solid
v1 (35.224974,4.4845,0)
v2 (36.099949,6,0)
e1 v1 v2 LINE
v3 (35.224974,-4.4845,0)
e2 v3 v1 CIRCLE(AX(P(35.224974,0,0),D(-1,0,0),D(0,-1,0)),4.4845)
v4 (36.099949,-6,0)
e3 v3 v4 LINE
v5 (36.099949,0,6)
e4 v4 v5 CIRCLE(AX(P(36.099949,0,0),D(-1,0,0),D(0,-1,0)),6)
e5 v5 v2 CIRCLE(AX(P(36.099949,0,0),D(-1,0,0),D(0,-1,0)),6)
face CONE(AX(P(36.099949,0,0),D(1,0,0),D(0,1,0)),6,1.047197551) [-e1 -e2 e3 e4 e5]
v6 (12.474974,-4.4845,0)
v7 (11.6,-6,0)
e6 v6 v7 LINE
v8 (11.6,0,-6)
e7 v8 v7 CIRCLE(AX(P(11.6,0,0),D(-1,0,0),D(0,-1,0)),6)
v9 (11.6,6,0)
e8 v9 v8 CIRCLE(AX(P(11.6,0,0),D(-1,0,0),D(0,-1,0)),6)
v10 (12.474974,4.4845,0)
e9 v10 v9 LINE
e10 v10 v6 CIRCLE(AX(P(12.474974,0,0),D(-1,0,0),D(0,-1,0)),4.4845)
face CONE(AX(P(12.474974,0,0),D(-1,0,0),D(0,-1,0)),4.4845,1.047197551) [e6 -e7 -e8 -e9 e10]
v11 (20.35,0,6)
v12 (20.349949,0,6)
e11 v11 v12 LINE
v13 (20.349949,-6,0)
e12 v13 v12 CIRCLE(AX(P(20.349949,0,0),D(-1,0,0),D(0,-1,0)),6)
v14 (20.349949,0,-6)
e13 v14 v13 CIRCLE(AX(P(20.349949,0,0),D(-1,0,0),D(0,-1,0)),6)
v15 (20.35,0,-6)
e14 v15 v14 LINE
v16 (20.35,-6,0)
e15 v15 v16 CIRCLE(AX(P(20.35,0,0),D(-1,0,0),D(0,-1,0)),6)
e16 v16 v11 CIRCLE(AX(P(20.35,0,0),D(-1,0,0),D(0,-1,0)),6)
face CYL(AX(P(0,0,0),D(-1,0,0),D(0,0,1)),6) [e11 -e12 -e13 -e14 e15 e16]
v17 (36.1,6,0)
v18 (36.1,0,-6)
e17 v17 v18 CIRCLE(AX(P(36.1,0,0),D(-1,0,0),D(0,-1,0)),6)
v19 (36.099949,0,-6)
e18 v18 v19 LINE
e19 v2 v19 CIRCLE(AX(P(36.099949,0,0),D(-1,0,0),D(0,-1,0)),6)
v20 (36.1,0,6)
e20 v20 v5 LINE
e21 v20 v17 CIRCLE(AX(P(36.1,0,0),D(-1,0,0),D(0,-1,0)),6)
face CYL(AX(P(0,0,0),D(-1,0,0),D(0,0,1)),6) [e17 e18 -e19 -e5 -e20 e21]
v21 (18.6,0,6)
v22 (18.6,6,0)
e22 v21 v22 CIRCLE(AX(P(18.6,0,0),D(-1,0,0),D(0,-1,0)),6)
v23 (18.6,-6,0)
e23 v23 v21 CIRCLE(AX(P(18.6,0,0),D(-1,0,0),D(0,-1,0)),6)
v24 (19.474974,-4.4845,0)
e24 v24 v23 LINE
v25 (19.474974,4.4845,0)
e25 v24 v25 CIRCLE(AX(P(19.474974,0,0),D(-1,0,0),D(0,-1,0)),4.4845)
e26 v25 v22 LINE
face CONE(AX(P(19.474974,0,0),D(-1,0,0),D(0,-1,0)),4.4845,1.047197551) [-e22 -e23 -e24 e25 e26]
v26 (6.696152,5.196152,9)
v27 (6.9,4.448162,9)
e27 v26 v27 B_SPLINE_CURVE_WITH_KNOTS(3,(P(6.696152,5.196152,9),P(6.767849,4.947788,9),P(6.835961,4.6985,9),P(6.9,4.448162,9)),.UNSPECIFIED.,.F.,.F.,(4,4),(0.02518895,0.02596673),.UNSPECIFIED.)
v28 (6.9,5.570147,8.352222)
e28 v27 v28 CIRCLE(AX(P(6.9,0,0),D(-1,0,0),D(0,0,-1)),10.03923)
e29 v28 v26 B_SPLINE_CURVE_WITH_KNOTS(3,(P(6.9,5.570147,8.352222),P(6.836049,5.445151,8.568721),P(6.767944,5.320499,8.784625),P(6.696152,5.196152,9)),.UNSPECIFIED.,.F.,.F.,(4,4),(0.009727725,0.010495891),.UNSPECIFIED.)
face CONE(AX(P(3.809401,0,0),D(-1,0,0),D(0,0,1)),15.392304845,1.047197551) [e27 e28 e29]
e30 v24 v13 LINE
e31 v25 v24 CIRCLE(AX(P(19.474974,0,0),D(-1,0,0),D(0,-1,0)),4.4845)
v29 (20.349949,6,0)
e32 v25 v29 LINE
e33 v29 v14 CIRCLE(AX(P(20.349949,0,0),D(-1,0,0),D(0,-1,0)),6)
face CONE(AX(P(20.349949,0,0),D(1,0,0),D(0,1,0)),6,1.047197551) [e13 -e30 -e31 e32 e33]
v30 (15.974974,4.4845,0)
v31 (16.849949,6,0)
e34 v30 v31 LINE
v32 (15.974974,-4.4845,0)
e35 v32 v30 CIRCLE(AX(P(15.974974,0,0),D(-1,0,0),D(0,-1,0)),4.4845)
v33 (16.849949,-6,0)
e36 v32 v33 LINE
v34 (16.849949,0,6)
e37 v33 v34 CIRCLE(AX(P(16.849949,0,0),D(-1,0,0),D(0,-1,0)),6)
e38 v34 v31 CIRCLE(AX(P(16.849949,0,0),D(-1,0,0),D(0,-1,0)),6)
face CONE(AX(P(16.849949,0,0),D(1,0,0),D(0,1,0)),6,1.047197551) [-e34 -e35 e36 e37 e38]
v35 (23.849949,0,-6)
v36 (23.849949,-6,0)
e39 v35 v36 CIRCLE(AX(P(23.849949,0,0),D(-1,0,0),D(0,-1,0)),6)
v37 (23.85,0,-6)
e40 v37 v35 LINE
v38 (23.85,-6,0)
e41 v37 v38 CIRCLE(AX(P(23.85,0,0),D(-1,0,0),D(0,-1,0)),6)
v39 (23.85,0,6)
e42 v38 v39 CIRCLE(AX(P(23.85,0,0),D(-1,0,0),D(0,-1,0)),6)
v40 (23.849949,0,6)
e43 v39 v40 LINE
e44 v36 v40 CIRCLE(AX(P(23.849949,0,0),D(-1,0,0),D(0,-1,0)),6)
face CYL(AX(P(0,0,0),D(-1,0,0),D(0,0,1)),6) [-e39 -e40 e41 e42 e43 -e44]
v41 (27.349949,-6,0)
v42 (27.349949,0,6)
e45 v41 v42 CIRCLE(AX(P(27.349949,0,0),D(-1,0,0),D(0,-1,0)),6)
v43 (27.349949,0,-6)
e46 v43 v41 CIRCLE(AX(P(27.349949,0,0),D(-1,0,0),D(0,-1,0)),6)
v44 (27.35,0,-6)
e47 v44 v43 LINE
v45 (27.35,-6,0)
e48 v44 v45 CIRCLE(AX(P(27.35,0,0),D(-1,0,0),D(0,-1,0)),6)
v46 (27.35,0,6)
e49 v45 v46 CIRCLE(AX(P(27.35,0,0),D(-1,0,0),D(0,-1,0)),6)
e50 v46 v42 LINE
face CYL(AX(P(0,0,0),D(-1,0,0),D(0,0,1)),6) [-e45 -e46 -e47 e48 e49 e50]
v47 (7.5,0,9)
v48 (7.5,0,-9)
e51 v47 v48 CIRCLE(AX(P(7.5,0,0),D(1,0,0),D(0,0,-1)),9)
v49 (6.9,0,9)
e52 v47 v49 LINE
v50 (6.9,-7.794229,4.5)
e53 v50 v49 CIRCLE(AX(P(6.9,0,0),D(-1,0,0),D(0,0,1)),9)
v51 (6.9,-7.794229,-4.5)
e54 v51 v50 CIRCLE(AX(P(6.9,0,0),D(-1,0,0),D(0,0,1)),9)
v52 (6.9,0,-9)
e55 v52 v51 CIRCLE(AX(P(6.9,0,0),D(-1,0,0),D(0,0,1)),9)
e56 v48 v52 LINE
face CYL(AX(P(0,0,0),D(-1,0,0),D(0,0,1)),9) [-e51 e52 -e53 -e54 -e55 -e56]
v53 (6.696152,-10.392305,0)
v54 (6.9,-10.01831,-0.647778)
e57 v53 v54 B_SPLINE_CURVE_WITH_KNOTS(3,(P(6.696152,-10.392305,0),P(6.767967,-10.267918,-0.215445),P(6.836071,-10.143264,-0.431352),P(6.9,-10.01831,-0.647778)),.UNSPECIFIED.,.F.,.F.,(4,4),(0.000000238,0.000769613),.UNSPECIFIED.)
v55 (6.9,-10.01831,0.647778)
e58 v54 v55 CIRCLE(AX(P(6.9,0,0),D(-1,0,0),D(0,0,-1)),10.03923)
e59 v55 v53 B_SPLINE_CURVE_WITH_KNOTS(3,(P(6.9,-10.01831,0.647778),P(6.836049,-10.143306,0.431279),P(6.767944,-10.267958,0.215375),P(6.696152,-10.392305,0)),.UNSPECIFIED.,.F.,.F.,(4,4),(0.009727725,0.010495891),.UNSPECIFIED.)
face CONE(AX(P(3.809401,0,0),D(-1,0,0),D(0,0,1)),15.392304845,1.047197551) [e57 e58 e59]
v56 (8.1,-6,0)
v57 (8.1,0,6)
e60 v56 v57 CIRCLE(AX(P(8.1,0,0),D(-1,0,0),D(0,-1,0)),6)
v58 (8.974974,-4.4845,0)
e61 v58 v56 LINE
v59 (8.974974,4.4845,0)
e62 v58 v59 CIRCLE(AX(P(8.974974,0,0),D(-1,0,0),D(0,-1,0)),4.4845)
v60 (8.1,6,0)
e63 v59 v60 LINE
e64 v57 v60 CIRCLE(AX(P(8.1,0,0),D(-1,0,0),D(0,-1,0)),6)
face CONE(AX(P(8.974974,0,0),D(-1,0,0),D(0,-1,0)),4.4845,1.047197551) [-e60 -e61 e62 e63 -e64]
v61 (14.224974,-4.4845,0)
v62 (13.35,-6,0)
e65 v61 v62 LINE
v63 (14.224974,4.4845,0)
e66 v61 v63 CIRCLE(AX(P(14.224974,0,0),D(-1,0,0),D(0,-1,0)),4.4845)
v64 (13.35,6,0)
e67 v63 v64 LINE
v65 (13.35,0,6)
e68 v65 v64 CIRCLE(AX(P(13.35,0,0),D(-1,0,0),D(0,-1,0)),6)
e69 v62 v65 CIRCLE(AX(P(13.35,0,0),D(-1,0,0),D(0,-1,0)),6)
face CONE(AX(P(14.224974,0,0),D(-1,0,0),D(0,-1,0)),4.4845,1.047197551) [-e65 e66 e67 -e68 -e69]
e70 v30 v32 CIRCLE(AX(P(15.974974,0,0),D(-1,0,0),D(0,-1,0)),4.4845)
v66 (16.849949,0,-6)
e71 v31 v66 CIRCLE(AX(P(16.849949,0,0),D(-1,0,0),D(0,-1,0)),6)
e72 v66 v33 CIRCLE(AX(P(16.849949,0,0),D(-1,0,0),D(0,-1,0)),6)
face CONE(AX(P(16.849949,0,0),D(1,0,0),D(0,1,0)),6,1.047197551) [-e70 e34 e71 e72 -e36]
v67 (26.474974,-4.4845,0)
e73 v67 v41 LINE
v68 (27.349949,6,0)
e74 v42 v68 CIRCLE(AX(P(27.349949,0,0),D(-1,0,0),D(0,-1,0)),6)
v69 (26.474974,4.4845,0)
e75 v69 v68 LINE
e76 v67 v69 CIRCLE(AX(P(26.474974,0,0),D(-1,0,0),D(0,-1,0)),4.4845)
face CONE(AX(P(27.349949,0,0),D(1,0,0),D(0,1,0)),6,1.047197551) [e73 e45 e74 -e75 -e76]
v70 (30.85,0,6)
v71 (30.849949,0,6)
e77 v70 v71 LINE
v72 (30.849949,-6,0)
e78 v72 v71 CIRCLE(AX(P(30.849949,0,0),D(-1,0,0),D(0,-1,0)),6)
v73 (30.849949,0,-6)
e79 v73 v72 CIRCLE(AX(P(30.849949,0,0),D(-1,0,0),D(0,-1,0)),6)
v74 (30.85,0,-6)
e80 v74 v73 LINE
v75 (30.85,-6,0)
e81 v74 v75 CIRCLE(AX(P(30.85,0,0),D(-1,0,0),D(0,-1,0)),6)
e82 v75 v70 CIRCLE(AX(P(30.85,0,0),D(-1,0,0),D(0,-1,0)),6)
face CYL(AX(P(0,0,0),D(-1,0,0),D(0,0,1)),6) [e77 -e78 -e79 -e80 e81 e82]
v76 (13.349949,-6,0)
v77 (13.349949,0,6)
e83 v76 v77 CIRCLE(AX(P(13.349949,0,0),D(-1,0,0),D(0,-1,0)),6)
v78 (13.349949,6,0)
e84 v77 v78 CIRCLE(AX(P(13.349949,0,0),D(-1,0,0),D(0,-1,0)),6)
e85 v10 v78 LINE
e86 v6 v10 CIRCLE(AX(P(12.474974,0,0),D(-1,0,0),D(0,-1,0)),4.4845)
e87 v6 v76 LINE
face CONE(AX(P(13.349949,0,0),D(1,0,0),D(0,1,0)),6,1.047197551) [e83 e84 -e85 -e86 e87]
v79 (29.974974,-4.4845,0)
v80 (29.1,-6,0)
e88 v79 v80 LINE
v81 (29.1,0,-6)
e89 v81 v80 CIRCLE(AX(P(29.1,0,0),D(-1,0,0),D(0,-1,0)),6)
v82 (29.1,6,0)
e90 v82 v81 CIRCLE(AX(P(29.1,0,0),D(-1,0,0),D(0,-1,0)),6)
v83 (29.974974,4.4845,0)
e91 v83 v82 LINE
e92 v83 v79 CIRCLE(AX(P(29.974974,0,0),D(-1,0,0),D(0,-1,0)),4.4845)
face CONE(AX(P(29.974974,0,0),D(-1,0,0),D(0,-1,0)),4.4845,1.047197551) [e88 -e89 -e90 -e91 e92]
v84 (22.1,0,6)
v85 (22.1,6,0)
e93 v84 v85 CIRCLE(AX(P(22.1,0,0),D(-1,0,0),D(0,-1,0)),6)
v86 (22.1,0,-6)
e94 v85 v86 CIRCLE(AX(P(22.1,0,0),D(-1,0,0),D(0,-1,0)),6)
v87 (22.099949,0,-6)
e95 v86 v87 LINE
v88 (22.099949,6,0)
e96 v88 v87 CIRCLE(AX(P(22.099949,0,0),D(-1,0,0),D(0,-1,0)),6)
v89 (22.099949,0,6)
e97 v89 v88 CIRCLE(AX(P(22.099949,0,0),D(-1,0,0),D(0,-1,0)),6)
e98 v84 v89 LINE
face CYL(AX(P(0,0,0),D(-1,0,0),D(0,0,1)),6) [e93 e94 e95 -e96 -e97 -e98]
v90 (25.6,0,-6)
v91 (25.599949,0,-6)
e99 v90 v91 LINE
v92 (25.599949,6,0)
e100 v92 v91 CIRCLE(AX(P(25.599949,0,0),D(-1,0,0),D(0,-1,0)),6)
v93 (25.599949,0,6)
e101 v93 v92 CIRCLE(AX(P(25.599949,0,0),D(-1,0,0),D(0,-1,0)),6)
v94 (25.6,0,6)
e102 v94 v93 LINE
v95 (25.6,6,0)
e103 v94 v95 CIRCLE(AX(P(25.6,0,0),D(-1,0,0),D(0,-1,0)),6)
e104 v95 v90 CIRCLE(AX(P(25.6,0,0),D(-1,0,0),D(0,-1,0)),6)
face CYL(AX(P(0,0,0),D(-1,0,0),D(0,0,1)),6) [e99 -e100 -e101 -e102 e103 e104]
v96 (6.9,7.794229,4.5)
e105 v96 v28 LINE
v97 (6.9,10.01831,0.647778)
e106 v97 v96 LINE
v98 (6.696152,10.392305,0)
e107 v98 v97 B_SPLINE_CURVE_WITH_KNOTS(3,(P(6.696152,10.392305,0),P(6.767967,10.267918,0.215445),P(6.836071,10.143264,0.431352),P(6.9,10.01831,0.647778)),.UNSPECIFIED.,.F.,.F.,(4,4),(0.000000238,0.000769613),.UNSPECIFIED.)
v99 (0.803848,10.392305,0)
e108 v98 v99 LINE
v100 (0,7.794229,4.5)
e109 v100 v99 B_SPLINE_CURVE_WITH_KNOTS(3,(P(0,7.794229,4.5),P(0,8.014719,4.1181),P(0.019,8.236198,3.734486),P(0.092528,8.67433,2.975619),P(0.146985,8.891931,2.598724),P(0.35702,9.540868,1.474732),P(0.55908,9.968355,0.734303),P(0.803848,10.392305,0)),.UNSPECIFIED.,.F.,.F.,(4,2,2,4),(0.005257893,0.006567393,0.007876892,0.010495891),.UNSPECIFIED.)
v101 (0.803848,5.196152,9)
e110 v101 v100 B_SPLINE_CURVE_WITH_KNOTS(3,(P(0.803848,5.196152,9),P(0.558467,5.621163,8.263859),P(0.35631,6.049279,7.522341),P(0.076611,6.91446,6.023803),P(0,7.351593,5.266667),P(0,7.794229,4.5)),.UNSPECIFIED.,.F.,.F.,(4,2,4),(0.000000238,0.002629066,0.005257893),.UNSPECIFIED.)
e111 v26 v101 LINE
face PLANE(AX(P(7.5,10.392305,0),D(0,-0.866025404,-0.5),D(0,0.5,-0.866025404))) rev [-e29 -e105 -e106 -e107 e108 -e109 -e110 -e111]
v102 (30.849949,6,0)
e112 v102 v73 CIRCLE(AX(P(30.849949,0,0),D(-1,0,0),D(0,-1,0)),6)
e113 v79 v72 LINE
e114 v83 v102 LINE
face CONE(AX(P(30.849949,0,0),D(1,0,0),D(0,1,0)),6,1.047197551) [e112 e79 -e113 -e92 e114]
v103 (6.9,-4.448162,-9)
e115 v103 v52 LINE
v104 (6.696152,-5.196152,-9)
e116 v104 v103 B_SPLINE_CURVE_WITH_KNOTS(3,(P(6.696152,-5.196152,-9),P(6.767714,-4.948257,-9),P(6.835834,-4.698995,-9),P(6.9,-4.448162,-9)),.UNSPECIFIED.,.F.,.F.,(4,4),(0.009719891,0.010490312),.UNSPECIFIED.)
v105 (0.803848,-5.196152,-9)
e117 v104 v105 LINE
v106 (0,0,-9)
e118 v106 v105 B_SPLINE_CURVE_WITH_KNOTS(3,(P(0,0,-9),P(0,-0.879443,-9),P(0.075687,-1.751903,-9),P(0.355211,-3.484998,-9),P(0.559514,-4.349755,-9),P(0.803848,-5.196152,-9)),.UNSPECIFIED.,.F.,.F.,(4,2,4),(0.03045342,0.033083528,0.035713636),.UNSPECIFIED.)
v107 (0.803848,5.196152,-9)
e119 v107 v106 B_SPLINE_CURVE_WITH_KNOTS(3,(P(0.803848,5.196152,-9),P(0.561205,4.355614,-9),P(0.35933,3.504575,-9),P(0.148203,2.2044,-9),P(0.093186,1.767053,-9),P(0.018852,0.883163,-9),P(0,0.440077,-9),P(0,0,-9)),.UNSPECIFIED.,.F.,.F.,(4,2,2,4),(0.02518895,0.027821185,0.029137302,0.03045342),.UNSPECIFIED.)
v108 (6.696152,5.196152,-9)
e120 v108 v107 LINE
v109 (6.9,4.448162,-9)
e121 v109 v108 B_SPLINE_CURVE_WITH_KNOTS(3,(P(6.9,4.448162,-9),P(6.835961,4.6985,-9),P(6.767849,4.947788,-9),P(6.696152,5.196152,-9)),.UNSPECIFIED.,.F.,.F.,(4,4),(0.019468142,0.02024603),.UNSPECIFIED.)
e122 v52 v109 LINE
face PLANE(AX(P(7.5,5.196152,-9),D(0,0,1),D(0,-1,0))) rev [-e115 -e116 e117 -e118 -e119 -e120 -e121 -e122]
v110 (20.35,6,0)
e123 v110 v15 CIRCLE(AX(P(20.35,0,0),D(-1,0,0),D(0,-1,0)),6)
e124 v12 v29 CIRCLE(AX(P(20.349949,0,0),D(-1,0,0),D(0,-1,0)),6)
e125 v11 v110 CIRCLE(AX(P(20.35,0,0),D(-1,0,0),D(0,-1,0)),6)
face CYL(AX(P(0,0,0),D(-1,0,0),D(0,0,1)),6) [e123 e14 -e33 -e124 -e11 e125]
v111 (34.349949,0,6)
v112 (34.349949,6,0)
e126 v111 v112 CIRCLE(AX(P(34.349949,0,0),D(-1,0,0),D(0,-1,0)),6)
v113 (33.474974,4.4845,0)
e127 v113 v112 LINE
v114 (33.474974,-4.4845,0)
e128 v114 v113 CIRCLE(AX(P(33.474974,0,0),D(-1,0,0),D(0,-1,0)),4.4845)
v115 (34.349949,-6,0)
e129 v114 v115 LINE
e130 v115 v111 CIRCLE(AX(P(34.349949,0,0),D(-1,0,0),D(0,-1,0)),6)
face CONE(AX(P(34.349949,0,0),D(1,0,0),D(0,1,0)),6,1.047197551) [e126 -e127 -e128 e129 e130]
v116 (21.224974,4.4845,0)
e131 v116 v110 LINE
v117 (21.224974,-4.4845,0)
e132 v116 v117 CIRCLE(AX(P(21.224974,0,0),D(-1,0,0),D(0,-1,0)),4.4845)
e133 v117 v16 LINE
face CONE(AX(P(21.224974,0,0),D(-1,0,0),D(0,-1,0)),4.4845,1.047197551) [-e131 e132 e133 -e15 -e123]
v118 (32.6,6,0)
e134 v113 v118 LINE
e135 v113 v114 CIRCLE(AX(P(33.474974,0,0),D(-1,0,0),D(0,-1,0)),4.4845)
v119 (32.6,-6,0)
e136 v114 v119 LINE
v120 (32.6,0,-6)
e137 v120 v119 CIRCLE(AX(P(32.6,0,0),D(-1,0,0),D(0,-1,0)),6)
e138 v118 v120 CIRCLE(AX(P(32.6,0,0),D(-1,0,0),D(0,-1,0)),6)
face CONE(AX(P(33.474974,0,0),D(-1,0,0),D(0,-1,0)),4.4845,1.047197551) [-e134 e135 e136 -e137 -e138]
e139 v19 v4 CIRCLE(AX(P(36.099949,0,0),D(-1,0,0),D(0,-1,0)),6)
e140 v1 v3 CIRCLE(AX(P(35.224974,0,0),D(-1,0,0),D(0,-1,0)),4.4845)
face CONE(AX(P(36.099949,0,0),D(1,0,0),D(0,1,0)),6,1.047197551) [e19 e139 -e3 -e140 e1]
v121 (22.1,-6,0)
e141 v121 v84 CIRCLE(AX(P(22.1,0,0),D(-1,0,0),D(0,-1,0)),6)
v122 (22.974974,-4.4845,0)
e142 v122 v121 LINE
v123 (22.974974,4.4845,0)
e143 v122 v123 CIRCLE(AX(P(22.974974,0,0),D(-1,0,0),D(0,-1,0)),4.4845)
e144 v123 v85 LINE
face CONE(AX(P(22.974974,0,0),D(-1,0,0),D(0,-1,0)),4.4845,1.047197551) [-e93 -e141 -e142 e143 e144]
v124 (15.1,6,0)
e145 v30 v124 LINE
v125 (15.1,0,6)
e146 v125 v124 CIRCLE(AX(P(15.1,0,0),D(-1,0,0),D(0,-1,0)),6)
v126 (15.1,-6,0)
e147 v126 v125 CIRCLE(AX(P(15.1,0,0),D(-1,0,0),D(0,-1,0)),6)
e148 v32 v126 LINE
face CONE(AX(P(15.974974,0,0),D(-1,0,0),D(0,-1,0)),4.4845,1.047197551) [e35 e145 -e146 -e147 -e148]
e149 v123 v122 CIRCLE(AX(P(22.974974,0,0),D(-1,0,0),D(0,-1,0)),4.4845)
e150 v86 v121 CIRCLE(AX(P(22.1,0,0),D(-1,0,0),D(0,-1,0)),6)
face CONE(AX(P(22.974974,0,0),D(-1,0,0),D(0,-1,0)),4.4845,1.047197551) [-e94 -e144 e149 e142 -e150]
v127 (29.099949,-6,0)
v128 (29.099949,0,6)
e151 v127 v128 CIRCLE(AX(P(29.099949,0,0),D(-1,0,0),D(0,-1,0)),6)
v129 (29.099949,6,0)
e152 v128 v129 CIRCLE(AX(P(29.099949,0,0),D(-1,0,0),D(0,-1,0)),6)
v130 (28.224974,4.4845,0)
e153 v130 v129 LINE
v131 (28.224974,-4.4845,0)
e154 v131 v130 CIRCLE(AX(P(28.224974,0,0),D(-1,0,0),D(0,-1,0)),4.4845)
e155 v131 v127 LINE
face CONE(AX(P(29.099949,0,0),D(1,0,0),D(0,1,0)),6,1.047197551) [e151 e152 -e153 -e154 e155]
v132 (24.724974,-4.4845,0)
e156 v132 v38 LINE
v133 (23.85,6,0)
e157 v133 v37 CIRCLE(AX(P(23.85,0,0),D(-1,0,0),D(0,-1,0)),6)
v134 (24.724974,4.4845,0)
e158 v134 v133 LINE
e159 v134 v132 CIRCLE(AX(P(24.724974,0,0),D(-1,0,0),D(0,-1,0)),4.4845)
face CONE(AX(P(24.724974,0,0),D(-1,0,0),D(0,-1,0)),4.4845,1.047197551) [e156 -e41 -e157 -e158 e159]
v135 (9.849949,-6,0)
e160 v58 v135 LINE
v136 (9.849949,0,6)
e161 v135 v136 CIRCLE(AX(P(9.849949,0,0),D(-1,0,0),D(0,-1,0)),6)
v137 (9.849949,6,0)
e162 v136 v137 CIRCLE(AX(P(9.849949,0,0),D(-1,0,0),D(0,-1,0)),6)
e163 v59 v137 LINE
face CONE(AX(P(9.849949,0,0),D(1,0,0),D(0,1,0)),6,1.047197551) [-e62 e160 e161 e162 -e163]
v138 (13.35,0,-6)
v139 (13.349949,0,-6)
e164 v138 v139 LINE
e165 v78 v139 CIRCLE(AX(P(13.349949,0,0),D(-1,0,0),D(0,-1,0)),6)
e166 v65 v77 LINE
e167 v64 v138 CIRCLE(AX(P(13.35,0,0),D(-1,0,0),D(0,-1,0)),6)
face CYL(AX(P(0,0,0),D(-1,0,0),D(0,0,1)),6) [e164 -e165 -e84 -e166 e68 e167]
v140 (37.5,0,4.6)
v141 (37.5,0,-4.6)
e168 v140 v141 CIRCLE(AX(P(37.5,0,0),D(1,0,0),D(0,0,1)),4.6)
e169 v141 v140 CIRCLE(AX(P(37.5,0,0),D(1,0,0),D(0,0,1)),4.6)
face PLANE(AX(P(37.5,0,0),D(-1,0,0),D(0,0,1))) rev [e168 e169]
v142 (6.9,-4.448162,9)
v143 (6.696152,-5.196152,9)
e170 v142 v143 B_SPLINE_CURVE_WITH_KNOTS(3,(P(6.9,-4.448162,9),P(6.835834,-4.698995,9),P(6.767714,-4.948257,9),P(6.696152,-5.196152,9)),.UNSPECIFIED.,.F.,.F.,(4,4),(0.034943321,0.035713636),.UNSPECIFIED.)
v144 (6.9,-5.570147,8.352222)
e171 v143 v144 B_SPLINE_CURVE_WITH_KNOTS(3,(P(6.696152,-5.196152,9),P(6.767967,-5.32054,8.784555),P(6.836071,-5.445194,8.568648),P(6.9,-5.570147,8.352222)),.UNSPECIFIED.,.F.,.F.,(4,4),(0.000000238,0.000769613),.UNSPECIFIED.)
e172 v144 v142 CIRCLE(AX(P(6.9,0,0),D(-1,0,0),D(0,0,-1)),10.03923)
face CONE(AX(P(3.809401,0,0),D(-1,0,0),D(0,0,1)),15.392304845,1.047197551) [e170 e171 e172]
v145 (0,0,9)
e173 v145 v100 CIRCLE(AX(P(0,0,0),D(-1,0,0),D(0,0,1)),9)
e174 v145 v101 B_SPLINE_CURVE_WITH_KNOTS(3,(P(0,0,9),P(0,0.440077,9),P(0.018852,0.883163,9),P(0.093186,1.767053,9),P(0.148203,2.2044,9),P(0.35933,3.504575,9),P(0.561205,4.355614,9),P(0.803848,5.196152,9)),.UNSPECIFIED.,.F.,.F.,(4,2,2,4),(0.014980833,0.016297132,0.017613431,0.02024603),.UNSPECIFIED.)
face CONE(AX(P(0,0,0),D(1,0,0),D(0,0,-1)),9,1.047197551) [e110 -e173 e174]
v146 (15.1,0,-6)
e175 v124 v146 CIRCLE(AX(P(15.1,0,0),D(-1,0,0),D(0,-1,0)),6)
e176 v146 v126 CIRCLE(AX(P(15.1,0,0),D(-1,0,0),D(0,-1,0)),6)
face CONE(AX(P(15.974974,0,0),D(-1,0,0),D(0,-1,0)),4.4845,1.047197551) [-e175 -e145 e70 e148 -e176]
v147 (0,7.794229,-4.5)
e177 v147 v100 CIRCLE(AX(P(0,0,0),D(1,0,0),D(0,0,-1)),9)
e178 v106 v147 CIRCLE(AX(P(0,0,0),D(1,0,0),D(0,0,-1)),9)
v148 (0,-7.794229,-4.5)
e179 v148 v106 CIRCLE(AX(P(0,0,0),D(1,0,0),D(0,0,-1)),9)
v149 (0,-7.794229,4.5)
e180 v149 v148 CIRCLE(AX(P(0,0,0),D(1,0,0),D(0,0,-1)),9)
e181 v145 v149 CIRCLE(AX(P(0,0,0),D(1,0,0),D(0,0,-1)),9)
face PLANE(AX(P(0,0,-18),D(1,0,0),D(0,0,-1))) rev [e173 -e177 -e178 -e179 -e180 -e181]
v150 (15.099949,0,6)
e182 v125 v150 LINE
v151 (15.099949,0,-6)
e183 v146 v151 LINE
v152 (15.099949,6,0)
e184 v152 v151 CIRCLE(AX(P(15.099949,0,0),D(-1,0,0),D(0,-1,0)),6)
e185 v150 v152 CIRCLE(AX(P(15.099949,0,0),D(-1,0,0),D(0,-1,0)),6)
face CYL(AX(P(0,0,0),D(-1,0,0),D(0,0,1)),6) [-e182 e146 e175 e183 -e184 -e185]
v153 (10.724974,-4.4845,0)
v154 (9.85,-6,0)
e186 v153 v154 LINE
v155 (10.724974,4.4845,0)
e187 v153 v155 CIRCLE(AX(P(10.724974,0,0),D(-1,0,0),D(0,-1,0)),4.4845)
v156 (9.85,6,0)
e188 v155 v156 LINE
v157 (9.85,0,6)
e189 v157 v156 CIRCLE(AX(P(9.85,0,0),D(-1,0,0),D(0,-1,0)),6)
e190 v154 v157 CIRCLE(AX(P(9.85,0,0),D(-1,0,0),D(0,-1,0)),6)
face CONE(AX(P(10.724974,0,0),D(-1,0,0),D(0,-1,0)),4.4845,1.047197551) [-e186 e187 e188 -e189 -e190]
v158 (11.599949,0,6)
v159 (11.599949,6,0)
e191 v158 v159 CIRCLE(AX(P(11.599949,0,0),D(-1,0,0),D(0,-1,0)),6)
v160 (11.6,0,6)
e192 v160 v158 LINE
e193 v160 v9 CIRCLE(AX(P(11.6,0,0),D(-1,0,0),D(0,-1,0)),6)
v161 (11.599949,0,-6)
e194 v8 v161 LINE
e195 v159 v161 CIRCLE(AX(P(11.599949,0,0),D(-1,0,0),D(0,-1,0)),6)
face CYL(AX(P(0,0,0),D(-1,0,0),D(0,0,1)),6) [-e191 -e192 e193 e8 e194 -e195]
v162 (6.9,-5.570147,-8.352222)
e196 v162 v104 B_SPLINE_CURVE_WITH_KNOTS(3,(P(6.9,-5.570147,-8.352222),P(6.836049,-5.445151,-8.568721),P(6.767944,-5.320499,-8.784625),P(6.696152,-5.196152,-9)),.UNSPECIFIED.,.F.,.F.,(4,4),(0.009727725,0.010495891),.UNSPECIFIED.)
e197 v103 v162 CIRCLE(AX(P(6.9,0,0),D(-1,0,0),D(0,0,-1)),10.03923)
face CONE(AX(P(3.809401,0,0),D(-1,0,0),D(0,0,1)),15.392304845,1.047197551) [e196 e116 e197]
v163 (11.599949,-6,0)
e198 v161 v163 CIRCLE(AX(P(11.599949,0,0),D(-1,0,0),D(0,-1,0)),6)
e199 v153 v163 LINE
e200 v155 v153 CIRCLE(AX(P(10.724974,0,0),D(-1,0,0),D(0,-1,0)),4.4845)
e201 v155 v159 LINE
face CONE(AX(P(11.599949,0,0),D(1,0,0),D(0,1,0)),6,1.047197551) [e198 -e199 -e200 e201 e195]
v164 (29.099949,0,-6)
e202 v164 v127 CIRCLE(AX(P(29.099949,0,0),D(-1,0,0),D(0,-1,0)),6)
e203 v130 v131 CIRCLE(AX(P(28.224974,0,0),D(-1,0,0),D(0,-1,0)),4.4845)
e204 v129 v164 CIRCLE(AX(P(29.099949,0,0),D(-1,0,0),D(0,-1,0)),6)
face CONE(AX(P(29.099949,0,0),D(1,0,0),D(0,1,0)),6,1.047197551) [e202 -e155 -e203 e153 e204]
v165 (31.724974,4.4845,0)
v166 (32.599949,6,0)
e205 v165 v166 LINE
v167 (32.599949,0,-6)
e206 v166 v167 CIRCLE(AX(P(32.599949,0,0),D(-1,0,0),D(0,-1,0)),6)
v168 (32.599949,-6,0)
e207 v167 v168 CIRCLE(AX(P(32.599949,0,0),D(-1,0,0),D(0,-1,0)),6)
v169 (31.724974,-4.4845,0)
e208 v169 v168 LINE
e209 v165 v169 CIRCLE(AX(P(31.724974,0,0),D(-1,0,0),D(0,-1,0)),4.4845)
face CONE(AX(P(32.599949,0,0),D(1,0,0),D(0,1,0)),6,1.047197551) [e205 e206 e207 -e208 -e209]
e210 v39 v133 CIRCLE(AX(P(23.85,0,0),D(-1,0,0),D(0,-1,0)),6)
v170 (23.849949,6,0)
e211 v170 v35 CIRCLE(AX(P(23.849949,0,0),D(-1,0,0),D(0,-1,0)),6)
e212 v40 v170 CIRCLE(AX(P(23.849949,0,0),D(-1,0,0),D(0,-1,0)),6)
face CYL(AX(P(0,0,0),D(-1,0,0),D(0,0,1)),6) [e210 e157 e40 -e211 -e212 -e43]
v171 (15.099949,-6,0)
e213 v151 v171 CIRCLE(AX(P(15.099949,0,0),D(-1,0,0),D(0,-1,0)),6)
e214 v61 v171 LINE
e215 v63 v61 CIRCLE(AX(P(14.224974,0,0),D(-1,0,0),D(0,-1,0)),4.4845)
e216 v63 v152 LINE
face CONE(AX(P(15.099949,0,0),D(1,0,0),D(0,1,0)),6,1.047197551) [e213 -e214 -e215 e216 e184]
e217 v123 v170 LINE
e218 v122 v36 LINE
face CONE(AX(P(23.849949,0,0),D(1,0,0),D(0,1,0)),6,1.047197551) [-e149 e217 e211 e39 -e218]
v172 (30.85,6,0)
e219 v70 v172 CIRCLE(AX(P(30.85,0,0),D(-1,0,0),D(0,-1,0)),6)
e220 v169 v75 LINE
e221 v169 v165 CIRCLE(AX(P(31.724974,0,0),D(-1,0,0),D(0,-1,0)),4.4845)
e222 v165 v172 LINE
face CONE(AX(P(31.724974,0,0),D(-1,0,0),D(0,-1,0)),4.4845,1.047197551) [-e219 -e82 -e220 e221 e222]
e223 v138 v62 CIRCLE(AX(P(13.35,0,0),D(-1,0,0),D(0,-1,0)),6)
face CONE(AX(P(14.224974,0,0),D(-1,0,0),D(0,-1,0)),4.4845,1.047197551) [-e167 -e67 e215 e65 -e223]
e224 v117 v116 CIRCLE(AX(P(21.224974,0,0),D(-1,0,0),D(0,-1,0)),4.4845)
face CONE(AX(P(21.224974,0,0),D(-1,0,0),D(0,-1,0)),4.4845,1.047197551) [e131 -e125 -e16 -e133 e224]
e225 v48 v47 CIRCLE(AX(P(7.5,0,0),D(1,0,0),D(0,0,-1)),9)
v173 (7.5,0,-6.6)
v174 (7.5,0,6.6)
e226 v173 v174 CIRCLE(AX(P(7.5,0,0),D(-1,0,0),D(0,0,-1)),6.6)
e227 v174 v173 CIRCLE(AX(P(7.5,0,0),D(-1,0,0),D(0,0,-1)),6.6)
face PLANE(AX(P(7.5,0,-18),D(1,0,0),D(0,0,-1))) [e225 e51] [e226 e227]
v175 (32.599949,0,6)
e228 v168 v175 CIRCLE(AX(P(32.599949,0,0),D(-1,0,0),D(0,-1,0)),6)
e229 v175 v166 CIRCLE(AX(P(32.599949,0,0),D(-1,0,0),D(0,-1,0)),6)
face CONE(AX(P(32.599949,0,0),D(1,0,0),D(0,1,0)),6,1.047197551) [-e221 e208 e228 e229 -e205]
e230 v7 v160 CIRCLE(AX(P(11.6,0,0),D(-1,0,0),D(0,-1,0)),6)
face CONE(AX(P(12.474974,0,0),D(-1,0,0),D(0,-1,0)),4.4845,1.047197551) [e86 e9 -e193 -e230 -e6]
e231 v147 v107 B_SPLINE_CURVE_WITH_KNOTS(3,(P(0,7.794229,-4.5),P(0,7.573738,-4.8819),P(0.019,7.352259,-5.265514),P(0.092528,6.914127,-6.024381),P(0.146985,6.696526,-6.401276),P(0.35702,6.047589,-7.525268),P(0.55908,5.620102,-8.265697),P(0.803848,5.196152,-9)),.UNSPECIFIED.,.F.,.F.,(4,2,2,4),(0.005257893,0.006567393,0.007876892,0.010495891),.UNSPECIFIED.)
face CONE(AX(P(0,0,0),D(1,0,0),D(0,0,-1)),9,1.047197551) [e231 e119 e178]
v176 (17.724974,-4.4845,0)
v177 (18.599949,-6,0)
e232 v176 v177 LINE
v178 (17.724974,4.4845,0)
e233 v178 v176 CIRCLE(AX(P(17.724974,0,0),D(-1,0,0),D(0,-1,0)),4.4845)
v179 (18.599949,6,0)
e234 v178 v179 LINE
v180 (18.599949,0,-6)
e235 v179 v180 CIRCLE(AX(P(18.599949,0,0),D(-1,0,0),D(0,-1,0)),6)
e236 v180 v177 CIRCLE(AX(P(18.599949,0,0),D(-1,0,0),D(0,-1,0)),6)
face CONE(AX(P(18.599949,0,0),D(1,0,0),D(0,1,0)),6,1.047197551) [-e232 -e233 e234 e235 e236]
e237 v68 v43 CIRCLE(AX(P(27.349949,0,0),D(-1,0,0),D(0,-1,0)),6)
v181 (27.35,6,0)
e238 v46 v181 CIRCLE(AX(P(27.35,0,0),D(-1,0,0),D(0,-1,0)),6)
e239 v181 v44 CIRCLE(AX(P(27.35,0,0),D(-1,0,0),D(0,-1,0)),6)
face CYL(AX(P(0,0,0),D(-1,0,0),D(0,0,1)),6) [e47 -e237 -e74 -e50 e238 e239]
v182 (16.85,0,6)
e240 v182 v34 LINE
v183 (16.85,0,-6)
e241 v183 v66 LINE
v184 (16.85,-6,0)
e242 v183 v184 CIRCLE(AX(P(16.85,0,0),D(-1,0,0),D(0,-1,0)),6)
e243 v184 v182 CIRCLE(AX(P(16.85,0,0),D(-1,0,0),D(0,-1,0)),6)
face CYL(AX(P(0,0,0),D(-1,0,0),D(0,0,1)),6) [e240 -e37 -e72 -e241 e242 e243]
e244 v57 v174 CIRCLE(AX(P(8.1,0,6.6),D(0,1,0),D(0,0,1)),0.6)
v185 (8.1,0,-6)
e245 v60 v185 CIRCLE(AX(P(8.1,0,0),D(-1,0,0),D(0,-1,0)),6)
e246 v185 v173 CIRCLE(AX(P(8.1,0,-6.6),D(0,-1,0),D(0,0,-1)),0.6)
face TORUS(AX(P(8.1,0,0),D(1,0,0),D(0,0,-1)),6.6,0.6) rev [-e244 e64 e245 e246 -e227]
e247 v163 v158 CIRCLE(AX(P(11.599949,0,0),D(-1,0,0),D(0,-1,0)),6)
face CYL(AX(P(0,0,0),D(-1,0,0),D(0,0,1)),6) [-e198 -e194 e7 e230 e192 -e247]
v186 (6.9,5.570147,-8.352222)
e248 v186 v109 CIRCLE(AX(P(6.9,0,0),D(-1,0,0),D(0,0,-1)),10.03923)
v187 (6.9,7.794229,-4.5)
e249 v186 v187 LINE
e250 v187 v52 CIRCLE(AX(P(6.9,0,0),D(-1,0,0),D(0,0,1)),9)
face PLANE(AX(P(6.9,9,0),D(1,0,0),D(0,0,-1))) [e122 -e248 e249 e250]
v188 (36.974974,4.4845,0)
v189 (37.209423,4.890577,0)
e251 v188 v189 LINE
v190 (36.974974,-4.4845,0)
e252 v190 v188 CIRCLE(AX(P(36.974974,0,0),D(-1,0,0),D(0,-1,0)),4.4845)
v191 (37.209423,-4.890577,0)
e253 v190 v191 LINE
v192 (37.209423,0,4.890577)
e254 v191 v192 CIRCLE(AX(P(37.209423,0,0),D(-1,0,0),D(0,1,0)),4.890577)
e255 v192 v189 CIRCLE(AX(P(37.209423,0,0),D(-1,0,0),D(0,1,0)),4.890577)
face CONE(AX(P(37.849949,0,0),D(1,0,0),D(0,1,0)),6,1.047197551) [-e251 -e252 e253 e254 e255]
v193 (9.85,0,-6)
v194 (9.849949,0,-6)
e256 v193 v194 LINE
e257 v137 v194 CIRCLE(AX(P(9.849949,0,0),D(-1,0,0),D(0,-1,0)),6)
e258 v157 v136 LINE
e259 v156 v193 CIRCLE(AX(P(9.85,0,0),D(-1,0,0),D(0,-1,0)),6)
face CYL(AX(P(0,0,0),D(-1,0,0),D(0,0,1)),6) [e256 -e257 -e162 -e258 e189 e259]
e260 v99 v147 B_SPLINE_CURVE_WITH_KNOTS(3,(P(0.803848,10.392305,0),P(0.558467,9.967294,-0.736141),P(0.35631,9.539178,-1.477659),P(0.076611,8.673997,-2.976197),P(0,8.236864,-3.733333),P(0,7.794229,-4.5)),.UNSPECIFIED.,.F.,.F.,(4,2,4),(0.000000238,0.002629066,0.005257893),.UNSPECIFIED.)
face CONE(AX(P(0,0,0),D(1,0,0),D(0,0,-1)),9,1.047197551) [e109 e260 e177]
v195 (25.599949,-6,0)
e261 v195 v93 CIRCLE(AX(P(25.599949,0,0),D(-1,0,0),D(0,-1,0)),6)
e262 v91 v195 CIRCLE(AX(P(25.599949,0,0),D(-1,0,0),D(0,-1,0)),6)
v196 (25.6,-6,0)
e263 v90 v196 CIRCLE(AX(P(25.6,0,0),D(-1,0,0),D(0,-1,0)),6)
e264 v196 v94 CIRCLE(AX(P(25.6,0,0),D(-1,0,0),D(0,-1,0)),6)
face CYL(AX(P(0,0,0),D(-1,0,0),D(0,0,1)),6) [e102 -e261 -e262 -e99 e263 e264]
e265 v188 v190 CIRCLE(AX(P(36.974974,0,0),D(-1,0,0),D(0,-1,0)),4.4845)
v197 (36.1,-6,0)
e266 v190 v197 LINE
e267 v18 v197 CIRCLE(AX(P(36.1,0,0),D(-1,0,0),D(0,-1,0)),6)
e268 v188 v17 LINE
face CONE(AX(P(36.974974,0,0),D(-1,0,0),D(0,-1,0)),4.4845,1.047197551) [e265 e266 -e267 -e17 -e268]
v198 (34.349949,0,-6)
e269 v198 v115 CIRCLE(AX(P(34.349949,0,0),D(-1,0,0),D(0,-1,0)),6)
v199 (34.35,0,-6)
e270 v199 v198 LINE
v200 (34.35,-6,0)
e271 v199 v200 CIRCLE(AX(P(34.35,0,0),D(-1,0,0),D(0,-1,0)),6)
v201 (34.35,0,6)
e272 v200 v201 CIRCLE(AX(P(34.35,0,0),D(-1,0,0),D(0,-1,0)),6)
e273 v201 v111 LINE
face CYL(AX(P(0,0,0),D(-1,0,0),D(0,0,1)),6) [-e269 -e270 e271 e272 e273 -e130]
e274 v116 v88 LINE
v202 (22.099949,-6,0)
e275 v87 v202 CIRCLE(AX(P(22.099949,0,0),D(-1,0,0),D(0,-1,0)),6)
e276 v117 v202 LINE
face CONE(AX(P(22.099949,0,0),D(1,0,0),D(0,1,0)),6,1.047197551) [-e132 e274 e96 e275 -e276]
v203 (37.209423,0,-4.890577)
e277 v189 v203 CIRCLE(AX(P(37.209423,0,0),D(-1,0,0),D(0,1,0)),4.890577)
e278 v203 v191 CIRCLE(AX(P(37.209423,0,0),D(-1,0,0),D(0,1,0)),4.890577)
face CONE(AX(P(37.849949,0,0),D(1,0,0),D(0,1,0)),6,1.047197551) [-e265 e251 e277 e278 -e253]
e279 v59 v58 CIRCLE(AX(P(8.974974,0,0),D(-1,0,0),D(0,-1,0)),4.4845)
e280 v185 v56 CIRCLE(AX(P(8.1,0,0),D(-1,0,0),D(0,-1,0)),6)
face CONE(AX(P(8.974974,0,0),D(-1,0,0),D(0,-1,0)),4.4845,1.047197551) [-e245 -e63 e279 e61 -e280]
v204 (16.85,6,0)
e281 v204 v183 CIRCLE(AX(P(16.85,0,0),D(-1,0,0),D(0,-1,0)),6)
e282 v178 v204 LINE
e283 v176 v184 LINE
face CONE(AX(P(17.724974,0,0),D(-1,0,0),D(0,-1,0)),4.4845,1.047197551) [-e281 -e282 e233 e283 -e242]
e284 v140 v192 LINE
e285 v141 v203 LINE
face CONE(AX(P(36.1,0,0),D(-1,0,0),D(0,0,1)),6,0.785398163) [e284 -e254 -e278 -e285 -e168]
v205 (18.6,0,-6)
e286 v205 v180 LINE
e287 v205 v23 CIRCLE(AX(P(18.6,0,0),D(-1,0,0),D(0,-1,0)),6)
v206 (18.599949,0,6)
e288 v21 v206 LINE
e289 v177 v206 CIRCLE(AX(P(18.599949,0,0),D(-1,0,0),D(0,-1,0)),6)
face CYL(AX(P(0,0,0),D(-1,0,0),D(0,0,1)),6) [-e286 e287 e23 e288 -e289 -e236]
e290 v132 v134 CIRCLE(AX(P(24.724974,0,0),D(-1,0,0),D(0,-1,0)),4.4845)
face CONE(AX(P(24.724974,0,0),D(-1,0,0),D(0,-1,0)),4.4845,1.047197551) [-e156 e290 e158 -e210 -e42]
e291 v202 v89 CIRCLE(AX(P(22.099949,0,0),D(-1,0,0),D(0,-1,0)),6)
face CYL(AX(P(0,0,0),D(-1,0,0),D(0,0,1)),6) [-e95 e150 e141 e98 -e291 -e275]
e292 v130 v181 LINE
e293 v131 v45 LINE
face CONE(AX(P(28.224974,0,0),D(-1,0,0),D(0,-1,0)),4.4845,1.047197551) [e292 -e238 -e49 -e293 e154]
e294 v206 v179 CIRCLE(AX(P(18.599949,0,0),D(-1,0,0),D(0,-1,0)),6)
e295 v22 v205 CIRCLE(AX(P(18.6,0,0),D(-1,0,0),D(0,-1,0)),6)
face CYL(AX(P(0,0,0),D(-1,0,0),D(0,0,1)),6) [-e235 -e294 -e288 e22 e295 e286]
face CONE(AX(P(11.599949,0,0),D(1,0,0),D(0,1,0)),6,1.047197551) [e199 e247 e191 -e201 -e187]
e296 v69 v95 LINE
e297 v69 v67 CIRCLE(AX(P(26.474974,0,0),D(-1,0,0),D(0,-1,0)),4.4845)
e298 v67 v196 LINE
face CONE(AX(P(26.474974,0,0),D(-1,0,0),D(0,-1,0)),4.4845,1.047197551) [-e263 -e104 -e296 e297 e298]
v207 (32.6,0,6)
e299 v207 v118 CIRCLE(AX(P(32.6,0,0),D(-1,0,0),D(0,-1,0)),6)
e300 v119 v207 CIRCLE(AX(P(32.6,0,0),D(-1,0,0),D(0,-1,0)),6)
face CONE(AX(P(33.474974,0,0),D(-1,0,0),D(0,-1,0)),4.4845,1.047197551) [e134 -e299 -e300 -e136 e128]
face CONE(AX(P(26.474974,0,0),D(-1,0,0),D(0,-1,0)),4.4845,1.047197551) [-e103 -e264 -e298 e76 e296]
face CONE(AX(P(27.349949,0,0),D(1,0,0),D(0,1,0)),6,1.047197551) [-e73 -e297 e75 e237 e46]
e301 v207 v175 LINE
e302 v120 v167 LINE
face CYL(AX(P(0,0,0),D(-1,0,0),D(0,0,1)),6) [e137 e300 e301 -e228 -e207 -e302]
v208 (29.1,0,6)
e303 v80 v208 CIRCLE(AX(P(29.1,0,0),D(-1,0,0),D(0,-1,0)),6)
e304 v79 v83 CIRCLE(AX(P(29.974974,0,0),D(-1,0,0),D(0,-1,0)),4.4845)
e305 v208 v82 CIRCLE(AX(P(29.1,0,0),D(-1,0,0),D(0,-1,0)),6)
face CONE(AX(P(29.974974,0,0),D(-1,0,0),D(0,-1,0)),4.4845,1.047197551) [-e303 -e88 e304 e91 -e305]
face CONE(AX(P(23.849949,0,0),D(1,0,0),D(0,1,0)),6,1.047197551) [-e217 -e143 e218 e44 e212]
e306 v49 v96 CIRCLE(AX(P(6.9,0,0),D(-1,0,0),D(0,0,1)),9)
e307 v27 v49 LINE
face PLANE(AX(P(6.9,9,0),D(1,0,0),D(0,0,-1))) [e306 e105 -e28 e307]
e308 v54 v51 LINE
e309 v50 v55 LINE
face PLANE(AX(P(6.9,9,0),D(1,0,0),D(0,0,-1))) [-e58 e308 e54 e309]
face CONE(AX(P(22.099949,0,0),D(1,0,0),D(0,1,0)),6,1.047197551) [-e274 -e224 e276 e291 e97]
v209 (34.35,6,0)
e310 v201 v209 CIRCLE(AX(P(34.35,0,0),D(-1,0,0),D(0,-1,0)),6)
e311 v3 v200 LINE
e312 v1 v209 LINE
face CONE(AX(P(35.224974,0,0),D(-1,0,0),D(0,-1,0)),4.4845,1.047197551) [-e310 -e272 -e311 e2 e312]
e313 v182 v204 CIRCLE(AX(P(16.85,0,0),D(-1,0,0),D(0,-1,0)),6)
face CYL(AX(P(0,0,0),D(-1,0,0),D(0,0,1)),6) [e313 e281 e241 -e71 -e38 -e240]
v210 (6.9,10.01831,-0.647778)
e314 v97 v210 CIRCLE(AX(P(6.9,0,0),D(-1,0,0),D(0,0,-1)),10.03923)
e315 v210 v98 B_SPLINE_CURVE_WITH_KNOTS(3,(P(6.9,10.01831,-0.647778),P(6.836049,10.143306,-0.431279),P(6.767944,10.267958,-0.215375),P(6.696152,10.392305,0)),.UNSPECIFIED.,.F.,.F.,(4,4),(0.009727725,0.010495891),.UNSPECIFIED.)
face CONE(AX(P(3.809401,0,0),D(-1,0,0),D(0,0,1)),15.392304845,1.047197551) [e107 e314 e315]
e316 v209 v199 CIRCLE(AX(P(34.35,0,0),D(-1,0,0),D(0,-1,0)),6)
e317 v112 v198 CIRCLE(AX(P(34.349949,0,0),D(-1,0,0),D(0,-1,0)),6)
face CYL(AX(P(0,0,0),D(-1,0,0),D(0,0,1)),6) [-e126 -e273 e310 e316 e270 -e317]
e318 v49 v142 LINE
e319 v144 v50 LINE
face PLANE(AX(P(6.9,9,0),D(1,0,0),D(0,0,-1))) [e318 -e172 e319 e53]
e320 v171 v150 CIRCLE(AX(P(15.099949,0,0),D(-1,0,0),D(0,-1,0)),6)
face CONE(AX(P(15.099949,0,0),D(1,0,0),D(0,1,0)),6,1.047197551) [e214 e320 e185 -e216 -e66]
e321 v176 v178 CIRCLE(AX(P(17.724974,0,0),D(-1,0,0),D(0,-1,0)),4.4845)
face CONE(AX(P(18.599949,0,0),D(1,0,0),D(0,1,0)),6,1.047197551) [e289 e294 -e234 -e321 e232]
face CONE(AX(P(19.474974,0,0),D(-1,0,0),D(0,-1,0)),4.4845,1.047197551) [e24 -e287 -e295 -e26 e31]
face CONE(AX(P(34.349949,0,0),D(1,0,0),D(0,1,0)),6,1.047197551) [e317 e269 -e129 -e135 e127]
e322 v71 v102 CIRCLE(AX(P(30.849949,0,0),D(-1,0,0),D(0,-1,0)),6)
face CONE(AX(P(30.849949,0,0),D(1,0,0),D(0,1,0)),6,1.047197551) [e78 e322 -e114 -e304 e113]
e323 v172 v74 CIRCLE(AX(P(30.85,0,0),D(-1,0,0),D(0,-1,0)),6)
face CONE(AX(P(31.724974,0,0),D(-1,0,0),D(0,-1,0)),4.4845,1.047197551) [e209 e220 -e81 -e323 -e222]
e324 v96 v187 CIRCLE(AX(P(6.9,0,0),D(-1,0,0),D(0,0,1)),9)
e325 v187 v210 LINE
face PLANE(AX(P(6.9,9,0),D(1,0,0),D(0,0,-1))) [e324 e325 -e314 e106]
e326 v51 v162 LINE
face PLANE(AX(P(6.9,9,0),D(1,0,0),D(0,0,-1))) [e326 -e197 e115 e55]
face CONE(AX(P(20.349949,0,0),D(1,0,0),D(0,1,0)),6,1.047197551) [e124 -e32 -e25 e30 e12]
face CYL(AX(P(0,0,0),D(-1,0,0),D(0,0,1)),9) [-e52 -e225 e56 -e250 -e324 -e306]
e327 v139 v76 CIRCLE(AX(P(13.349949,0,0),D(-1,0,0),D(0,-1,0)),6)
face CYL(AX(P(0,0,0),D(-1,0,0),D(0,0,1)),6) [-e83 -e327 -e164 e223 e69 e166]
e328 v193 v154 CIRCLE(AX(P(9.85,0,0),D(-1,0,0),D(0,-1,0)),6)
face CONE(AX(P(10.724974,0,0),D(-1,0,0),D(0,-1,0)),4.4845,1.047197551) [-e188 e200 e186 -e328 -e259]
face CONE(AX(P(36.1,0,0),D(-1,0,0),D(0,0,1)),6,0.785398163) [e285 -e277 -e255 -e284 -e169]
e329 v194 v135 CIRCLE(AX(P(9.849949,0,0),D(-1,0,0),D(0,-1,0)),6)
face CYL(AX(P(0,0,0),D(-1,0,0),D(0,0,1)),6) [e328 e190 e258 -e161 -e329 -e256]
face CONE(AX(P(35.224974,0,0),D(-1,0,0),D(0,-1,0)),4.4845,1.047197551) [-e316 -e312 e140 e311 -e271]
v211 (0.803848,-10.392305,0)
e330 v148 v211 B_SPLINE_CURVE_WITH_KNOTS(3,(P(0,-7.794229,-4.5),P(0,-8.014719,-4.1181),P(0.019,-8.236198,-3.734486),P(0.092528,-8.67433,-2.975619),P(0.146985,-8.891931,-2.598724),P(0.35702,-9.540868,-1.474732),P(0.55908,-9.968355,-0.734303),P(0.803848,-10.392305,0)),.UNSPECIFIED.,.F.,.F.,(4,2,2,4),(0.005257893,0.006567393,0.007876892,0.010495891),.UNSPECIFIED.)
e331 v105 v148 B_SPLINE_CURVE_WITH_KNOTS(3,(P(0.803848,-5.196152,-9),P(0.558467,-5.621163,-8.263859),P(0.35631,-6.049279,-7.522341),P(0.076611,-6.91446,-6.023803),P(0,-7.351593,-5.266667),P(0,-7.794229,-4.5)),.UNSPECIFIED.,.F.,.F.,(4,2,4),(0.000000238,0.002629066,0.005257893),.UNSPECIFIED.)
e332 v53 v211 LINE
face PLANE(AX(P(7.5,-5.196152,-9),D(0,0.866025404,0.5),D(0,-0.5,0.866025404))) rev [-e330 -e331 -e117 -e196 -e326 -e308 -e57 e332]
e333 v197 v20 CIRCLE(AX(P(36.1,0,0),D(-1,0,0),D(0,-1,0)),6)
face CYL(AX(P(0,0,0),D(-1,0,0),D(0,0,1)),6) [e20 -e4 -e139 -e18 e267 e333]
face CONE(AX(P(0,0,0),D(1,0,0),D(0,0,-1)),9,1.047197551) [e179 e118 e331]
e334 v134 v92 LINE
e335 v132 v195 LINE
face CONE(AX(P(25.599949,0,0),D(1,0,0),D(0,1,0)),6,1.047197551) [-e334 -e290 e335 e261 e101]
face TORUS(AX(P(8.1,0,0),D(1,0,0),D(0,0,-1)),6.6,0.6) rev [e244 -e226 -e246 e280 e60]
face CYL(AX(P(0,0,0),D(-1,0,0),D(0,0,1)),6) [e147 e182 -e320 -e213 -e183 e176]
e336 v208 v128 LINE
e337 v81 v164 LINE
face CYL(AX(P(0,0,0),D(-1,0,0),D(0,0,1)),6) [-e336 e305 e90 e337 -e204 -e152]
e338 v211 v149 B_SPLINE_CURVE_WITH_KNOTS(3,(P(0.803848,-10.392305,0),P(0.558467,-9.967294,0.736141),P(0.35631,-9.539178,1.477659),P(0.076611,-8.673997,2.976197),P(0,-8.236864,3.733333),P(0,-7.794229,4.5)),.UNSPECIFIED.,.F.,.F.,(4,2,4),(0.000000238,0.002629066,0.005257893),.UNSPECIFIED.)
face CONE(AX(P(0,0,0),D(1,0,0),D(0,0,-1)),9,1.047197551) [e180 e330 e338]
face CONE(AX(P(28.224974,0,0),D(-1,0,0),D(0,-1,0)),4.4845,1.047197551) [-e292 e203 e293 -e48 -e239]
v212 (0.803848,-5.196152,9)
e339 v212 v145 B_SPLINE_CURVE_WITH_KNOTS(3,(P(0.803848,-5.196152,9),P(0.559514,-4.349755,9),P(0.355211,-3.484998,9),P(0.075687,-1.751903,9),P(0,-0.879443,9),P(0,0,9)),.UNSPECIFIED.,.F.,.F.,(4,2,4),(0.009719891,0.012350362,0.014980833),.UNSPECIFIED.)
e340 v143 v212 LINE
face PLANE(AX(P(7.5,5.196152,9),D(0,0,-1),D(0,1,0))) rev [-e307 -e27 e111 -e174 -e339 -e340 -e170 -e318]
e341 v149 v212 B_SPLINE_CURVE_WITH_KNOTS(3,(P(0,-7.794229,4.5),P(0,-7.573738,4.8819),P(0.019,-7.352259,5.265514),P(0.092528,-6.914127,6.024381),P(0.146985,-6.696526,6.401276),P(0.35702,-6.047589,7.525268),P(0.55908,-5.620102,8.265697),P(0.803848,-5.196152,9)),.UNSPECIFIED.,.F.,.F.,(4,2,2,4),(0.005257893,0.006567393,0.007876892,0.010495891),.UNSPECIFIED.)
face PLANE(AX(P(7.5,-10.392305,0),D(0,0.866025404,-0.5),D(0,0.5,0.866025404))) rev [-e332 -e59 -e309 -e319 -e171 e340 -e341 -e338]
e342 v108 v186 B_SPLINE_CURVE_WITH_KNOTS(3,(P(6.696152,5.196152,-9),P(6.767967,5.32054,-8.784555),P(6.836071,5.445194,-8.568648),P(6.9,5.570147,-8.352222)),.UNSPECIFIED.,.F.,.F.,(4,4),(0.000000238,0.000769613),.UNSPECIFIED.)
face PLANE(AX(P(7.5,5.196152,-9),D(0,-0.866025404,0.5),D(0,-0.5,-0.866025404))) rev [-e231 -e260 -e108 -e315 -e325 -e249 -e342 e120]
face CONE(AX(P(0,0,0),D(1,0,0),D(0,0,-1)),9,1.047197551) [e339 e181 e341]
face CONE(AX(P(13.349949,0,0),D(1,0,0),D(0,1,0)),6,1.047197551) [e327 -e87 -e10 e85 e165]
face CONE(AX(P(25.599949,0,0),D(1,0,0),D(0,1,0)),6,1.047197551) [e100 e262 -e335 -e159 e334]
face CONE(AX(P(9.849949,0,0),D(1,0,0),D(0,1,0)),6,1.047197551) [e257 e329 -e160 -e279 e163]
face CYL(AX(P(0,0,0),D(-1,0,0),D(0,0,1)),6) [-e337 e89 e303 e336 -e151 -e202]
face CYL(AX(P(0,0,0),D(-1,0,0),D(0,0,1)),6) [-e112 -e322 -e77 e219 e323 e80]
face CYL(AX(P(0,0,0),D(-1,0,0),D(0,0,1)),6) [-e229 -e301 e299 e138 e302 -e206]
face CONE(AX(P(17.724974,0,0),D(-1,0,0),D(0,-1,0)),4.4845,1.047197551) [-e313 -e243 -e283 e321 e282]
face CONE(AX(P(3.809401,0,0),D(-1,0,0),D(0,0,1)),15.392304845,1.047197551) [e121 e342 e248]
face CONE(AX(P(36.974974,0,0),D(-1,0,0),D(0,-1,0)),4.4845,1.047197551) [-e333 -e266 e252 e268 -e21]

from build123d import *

# Parameters (mm, degrees)
EXTRUDE_374_DEPTH      = 7.5
SKETCH_4_W             = 0.6
SKETCH_4_H             = 11.392304845
CHAMFER_1914_SIZE      = 1.4
FILLET_1959_R          = 0.6
PATTERN_LINEAR_1_COUNT = 17
PATTERN_LINEAR_1_PITCH = 1.75


with BuildPart() as part:
    # 草图1 → Extrude 374 (new body)
    with BuildSketch(Plane(origin=(0, 0, 0), x_dir=(0, 0, -1), z_dir=(1, 0, 0))):
        Polygon((9, 5.196152423), (9, -5.196152423), (0, -10.392304845), (-9, -5.196152423), (-9, 5.196152423), (0, 10.392304845), align=None)
    extrude(amount=EXTRUDE_374_DEPTH)

    # 草图2 → 凸台-旋转1 (revolve)
    with BuildSketch(Plane.XY, mode=Mode.PRIVATE) as revolve_1_sk:
        Polygon((0, 0), (37.5, 0), (37.5, 4.4845), (37.5, 6), (0, 6), align=None)
    revolve(revolve_1_sk.sketch.rotate(Axis((0, 0, 0), (1, 0, 0)), 90), axis=Axis((0, 0, 0), (1, 0, 0)))

    # 草图3 → 切除-旋转1 (revolve, cut)
    with BuildSketch(Plane.XY):
        Polygon((0, 9), (3.690598923, 15.392304845), (3.690598923, 20.392304845), (-10, 20.392304845), (-10, 9), align=None)
    revolve(axis=Axis((0, 0, 0), (1, 0, 0)), mode=Mode.SUBTRACT)

    # 草图5 → 切除-旋转2 (revolve, cut)
    with BuildSketch(Plane.XY):
        Polygon((7.5, 9), (3.809401077, 15.392304845), (3.809401077, 20.392304845), (13.809401077, 20.392304845), (13.809401077, 9), align=None)
    revolve(axis=Axis((0, 0, 0), (1, 0, 0)), mode=Mode.SUBTRACT)

    # 草图4 → 切除-旋转3 (revolve, cut)
    with BuildSketch(Plane.XY, mode=Mode.PRIVATE) as cut_revolve_3_sk:
        with Locations((7.2, 14.696152423)):
            Rectangle(SKETCH_4_W, SKETCH_4_H)
    revolve(cut_revolve_3_sk.sketch.rotate(Axis((0, 0, 0), (1, 0, 0)), 270), axis=Axis((0, 0, 0), (1, 0, 0)), mode=Mode.SUBTRACT)

    # Chamfer 1914
    chamfer_1914_edges = [part.edges().sort_by_distance(p)[0] for p in [
        (37.5, 0, -6),
    ]]
    chamfer(chamfer_1914_edges, length=CHAMFER_1914_SIZE)

    # Fillet 1959
    fillet_1959_edges = [part.edges().sort_by_distance(p)[0] for p in [
        (7.5, 0, -6),
    ]]
    fillet(fillet_1959_edges, radius=FILLET_1959_R)

    # 草图6 → 切除-旋转4 (revolve, cut)
    with BuildSketch(Plane.XY):
        Polygon((8.974974333, -4.4845), (8.1, -6), (8.1, -7.5), (9.849948666, -7.5), (9.849948666, -6), align=None)
    cut_revolve_4 = revolve(axis=Axis((-3.175, 0, 0), (1, 0, 0)), mode=Mode.SUBTRACT)

    # 阵列(线性)1: 切除-旋转4 ×17
    with Locations(*[(i * PATTERN_LINEAR_1_PITCH, 0, 0) for i in range(1, PATTERN_LINEAR_1_COUNT)]):
        add(cut_revolve_4, mode=Mode.SUBTRACT)


solid = part.part
